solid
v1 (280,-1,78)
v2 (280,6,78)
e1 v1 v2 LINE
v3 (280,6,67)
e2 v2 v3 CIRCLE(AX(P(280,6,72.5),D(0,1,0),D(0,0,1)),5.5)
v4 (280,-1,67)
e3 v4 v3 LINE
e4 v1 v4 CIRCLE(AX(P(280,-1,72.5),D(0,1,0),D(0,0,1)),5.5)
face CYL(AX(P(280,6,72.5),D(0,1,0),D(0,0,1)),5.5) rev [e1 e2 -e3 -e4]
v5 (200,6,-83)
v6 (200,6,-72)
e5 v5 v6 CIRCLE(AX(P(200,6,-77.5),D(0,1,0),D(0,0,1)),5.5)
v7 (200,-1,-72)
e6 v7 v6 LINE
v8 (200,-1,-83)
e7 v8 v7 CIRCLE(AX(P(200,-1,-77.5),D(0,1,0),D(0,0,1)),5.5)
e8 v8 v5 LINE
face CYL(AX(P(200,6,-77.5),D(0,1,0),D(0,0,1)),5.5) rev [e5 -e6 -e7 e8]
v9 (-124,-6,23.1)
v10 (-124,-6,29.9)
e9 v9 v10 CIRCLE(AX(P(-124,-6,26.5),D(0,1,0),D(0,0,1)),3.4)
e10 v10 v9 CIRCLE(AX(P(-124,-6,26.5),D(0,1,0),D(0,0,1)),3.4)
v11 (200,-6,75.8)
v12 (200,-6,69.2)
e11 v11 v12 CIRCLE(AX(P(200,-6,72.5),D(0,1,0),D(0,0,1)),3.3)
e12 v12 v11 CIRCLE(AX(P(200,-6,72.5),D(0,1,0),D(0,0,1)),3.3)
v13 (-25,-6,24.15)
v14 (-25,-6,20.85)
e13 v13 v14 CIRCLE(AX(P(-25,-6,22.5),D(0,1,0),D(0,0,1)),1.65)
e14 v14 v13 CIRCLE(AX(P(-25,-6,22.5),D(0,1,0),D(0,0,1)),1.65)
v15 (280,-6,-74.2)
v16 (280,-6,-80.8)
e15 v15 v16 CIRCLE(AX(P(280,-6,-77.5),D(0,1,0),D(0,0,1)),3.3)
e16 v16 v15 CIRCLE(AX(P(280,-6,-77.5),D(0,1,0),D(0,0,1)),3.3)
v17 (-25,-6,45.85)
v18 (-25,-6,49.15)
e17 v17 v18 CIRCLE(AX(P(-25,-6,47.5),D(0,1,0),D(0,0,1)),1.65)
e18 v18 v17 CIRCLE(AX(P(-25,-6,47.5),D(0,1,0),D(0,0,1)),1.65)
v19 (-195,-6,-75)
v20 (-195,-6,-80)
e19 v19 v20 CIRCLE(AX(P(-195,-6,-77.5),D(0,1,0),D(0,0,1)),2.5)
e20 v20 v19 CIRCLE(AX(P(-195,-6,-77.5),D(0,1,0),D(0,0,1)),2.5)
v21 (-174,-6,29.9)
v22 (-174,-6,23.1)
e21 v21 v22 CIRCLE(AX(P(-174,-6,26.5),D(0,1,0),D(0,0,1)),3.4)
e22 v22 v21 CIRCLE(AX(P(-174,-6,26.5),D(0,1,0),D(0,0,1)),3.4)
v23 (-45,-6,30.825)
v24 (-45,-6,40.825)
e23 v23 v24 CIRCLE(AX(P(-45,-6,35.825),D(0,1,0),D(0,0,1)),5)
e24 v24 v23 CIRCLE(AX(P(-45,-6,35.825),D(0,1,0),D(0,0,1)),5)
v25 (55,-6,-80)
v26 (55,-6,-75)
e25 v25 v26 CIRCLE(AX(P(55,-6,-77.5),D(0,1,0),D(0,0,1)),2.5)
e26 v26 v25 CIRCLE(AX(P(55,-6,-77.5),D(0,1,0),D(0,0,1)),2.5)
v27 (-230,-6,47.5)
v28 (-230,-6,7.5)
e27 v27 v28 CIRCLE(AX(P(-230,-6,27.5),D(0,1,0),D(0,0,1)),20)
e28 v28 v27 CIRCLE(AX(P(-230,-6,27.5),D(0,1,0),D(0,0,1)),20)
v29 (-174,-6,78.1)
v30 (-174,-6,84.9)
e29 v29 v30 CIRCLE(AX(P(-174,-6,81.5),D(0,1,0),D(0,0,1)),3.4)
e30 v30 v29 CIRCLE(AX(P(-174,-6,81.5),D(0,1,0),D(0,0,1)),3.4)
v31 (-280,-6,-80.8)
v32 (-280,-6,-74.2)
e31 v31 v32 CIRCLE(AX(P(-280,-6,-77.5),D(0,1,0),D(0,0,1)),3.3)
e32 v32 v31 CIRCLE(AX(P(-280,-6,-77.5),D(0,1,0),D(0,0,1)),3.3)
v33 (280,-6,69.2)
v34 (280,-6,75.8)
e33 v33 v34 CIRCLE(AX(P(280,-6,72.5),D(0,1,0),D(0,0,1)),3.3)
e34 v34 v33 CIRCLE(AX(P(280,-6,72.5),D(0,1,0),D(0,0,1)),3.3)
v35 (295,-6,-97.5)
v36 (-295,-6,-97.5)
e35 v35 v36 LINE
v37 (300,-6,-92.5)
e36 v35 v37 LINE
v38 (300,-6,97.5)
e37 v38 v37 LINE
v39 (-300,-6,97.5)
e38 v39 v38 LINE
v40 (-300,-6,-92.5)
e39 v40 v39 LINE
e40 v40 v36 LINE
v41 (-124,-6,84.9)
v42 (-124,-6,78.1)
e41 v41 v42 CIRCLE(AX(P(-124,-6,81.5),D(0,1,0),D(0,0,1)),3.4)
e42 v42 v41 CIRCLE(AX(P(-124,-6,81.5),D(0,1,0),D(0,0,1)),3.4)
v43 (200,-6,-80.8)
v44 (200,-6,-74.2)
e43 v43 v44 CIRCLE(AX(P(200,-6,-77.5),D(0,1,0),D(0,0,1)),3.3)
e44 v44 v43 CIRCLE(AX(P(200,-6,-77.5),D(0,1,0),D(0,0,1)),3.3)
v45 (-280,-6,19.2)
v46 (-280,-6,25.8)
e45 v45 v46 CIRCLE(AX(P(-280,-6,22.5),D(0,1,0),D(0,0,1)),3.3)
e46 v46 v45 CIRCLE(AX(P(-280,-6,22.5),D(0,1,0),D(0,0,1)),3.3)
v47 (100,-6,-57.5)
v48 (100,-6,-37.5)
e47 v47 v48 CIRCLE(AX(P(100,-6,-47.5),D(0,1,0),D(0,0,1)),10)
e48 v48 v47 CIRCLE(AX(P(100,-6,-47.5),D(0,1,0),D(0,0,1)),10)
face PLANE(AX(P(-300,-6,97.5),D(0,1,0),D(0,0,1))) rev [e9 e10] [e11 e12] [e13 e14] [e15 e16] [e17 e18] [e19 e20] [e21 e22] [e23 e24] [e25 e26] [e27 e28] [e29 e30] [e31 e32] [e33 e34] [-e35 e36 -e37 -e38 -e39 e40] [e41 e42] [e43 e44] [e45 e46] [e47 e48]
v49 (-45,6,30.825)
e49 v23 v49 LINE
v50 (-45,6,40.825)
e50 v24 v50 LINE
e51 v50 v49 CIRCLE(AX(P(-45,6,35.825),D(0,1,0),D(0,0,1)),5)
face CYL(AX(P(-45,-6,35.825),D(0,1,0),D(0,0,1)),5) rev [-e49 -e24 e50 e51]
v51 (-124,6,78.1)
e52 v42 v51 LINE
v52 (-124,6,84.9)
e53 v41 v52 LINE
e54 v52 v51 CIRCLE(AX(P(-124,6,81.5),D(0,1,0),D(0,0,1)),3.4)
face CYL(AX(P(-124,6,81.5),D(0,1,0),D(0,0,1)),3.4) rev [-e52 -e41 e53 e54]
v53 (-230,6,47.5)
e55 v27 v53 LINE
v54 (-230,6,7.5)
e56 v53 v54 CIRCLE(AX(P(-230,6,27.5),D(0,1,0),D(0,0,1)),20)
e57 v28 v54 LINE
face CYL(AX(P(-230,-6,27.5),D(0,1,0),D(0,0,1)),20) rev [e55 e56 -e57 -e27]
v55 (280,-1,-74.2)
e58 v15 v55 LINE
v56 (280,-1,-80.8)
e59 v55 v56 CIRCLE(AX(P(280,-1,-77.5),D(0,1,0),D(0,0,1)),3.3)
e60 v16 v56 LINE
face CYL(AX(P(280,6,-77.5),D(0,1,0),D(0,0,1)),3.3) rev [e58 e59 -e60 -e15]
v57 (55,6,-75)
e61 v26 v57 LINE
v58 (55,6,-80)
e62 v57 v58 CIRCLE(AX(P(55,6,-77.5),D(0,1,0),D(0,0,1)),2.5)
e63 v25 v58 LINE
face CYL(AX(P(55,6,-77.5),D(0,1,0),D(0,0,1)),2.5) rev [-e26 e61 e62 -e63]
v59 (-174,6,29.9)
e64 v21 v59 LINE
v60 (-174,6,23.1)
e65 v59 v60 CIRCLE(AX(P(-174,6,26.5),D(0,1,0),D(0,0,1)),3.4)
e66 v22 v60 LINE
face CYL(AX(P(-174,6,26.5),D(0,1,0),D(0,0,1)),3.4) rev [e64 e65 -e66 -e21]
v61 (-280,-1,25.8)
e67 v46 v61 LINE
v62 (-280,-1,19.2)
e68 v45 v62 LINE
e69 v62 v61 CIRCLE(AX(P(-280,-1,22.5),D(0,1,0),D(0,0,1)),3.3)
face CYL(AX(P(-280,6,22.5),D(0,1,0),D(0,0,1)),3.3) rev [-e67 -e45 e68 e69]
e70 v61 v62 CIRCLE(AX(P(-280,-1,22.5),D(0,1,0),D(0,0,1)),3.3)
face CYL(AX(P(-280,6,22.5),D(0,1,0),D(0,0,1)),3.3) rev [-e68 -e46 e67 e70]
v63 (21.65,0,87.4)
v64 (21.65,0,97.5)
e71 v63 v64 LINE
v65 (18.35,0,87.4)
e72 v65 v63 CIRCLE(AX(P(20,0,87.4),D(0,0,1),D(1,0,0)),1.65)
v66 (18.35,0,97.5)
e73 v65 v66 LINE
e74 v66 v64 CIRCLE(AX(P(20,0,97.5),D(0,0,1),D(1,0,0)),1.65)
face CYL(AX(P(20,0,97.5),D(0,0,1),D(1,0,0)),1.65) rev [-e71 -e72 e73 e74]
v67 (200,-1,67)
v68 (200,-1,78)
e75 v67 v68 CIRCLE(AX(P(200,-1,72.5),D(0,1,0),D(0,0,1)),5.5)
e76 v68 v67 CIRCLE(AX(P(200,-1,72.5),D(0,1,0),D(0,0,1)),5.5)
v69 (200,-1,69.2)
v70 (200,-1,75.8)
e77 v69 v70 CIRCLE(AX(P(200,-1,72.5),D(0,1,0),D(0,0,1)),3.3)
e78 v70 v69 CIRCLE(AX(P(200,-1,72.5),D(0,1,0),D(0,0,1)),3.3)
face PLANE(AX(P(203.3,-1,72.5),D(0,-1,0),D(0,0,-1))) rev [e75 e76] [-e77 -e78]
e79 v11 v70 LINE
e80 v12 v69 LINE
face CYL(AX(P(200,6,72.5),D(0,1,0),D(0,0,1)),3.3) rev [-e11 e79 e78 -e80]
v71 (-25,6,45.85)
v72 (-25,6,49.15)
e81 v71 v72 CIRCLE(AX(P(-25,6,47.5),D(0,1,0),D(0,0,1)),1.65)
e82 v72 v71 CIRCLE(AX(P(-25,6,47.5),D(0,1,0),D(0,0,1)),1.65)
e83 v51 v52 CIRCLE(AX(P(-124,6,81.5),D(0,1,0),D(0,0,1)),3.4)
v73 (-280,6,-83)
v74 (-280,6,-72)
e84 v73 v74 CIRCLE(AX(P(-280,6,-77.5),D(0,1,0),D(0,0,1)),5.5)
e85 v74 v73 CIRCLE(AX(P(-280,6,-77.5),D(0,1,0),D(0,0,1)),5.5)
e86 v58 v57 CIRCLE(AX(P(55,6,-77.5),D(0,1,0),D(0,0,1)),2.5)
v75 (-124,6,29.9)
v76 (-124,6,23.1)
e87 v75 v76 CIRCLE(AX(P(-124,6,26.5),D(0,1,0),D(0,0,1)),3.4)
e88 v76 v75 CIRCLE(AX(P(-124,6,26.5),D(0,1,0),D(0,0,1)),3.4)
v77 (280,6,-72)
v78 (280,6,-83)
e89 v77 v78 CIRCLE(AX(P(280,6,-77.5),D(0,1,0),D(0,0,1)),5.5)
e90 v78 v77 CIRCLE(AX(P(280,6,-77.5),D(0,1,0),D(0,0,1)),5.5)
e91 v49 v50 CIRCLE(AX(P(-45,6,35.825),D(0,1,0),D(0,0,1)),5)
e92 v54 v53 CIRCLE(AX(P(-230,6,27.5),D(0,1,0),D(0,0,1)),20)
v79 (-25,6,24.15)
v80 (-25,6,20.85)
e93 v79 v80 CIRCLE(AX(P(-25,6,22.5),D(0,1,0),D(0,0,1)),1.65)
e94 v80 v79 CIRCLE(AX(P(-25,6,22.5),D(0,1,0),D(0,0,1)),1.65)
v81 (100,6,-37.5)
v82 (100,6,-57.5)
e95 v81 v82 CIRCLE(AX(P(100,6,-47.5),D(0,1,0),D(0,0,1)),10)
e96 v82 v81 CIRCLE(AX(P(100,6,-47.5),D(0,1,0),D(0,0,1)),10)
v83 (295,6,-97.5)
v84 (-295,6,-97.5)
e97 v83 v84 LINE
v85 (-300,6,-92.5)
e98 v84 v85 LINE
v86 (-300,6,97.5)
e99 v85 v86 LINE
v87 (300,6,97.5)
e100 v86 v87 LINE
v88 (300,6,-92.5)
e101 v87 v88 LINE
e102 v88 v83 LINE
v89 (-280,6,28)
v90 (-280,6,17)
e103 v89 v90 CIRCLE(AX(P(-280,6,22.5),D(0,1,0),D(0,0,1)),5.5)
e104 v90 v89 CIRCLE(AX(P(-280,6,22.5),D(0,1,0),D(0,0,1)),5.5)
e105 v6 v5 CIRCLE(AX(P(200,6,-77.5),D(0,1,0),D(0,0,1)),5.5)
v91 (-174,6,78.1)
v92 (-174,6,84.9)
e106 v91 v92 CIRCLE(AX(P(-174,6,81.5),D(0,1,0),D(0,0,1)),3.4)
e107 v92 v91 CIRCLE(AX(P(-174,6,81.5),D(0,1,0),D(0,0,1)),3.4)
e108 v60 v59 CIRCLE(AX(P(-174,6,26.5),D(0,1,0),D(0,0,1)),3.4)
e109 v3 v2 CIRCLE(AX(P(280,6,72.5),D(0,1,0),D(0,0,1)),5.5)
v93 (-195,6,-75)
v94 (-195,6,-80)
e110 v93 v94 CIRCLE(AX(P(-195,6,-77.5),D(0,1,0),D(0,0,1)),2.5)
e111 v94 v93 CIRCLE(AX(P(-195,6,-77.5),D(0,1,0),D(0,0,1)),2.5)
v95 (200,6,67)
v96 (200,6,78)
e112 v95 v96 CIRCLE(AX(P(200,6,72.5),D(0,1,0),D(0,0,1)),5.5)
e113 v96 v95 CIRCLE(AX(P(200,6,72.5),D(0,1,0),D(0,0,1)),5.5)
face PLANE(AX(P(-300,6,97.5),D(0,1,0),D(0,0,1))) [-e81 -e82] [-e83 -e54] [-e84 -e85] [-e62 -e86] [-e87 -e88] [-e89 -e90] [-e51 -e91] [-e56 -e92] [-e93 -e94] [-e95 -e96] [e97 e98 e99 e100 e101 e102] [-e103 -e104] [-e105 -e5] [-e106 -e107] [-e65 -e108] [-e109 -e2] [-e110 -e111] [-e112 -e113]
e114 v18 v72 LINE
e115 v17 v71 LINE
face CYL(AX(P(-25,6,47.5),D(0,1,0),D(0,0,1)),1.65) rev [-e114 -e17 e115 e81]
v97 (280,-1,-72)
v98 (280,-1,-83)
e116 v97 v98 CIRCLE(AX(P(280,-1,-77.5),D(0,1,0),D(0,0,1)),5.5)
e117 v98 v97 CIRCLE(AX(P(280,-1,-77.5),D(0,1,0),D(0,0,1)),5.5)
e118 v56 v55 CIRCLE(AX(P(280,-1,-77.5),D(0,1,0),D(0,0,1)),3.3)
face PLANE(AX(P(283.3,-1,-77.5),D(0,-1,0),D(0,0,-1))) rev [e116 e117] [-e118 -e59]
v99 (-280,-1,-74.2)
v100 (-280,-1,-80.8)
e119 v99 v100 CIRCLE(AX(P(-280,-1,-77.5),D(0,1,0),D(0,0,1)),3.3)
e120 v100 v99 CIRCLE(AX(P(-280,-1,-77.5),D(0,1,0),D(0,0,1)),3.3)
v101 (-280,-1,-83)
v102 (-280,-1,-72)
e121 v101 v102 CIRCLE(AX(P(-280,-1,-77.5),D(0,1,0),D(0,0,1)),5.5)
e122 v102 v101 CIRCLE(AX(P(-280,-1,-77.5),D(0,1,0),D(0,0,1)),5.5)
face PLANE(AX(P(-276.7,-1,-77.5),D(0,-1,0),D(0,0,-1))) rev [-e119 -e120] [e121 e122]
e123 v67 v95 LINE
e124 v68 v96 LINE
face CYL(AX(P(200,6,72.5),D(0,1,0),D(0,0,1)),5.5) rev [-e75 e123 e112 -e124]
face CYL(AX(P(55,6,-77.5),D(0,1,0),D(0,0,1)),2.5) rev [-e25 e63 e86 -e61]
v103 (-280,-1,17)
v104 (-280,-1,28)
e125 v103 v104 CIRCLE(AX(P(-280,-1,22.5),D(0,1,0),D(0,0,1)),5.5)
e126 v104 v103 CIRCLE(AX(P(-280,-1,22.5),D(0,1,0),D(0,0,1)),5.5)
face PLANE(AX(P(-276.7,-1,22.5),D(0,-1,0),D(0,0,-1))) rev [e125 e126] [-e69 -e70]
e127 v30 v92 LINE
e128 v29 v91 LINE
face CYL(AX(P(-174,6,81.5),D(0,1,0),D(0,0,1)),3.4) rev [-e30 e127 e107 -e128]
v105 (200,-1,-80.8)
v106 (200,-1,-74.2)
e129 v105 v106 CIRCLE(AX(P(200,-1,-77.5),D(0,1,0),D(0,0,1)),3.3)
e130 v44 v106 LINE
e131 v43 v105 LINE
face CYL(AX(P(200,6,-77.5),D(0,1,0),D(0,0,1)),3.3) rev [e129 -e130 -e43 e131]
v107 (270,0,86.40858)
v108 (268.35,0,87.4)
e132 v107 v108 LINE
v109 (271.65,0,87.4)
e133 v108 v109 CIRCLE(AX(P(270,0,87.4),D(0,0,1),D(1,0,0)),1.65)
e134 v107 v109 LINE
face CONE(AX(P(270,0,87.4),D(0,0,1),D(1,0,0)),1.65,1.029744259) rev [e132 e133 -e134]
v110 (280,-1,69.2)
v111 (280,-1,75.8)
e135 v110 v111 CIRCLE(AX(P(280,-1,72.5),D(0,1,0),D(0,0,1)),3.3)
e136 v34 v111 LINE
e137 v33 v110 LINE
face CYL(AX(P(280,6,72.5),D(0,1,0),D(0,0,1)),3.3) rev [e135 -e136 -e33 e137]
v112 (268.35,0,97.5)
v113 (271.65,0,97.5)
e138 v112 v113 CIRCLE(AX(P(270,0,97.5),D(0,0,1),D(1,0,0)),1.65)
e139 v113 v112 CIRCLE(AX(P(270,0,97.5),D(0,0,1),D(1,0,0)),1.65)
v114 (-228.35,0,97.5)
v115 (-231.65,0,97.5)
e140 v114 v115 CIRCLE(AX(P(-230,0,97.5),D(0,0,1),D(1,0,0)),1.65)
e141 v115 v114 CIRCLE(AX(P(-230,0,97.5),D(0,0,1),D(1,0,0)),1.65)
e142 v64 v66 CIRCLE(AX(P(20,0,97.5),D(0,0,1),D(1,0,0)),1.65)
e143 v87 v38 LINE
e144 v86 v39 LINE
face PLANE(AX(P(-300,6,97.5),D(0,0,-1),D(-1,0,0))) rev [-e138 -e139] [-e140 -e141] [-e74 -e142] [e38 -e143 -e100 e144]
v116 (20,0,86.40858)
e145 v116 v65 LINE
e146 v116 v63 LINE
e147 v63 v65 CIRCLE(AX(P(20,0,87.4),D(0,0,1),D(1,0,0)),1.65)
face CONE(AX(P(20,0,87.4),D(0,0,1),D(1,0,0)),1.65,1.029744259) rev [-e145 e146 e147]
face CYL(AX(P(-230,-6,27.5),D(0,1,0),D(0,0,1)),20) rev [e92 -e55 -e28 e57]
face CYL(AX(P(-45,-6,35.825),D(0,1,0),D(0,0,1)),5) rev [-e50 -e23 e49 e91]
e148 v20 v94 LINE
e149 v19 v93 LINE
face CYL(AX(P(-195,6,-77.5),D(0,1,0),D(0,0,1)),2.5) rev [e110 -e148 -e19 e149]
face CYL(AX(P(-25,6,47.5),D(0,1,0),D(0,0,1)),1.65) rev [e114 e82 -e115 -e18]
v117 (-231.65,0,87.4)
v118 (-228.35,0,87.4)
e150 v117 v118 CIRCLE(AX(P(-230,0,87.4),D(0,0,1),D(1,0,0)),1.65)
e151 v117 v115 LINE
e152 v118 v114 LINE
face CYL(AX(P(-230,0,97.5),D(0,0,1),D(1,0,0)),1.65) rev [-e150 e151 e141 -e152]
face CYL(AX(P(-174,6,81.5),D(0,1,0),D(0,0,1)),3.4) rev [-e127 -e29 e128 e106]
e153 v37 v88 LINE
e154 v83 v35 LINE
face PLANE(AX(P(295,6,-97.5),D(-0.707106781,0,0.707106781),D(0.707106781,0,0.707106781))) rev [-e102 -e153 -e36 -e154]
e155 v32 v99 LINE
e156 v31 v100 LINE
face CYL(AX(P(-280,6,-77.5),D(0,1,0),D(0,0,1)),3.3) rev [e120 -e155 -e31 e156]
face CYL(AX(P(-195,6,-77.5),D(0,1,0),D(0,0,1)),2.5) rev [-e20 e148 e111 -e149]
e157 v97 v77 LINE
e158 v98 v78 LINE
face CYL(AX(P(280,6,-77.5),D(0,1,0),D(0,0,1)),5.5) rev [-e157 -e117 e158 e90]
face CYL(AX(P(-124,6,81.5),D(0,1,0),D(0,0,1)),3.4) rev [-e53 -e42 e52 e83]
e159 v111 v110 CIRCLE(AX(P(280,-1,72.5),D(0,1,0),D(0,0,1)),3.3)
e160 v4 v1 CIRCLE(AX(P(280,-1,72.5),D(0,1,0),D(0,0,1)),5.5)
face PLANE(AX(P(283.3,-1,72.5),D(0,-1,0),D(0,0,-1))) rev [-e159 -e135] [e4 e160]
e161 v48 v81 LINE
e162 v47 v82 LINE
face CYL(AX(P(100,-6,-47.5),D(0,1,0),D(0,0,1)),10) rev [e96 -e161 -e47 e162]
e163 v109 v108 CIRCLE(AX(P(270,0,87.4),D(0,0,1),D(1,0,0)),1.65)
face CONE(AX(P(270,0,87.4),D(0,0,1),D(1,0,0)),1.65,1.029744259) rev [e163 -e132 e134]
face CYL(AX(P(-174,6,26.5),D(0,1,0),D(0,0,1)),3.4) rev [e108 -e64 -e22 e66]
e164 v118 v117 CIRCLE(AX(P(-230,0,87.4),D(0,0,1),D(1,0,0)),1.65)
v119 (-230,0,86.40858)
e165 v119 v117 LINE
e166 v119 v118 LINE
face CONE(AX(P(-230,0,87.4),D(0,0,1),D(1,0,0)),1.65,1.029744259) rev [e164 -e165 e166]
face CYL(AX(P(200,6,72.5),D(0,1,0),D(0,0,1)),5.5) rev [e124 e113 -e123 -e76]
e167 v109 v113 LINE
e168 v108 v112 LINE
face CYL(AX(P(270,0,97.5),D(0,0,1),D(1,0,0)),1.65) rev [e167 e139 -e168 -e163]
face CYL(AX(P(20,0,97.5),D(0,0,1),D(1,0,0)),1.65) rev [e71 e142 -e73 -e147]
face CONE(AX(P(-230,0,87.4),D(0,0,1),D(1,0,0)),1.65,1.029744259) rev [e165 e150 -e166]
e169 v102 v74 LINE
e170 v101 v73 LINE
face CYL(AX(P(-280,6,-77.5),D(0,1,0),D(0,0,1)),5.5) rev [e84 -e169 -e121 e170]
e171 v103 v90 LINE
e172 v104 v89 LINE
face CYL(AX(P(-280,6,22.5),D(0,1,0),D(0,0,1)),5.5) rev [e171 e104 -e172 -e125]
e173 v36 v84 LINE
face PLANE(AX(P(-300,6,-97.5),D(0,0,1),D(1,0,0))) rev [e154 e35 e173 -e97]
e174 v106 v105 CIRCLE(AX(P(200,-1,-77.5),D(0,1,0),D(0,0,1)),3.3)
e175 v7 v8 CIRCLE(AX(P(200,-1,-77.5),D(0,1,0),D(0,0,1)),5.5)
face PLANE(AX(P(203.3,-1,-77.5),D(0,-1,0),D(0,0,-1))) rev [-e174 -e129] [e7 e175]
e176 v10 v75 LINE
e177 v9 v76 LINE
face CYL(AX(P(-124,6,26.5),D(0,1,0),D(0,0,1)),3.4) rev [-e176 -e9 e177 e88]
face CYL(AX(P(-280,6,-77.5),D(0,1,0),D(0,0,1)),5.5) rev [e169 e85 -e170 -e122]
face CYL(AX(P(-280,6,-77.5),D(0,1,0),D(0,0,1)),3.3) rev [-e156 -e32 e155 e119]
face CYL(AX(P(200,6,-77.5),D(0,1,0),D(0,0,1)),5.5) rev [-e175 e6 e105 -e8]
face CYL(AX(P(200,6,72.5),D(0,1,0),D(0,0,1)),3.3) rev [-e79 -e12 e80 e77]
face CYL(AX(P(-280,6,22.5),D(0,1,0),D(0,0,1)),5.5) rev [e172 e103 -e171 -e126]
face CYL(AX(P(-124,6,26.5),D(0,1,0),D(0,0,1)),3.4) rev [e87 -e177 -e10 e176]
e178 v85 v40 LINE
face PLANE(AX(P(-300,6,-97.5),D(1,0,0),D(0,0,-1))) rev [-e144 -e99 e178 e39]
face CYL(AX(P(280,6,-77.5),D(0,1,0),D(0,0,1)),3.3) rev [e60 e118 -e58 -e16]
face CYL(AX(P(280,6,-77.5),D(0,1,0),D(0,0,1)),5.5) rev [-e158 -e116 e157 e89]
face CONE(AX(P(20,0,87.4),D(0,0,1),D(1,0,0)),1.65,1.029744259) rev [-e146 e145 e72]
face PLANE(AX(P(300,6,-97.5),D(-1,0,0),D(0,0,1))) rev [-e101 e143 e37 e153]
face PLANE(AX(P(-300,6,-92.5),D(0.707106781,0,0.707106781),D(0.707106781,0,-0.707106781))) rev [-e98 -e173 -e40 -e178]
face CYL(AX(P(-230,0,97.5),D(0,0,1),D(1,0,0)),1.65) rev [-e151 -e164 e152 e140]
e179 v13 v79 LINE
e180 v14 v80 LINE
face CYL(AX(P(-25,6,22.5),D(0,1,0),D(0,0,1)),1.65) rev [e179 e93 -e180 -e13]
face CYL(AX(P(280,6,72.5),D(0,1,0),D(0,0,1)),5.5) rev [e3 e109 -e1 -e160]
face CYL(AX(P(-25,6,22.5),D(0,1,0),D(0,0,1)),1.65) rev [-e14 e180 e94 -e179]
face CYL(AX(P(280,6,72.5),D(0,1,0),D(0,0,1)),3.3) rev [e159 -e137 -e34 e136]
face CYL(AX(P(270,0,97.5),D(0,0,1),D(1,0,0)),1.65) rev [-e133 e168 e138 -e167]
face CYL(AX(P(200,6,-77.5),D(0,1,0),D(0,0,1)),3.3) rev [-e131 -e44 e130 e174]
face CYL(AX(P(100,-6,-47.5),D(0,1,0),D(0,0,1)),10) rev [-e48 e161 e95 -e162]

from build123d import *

# Parameters (mm, degrees)
SKETCH1_W                                         = 600
SKETCH1_H                                         = 195
EXTRUDE1_DEPTH                                    = 6
CHAMFER1_SIZE                                     = 5
M6_SOCKET_HEAD_CAP_SCREW_COUNTERBORE1_D           = 6.6
M6_SOCKET_HEAD_CAP_SCREW_COUNTERBORE1_CBORE_D     = 11
M6_SOCKET_HEAD_CAP_SCREW_COUNTERBORE1_CBORE_DEPTH = 7
M4_TAPPED_HOLE1_D                                 = 3.3
M4_TAPPED_HOLE1_DEPTH                             = 10.1
M4_TAPPED_HOLE1_TIP                               = 0.991420021
M8_TAPPED_HOLE1_D                                 = 6.8
M6_TAPPED_HOLE2_D                                 = 5
SKETCH10_R                                        = 20
CUT_EXTRUDE1_DEPTH                                = 316.674278331
SKETCH11_R                                        = 10
CUT_EXTRUDE2_DEPTH                                = 316.674278331
M4_TAPPED_HOLE2_D                                 = 3.3
M4_TAPPED_HOLE2_DEPTH                             = 12
M4_TAPPED_HOLE2_TIP                               = 0.991420021
SKETCH13_R                                        = 5
CUT_EXTRUDE3_DEPTH                                = 316.674278331


with BuildPart() as part:
    # Sketch1 → Extrude1 (new, symmetric)
    with BuildSketch(Plane(origin=(0, 0, 0), x_dir=(1, 0, 0), z_dir=(0, 1, 0))):
        Rectangle(SKETCH1_W, SKETCH1_H)
    extrude(amount=EXTRUDE1_DEPTH, both=True)

    # Chamfer1
    chamfer1_edges = [part.edges().sort_by_distance(p)[0] for p in [
        (-300, 0, -97.5),
        (300, 0, -97.5),
    ]]
    chamfer(chamfer1_edges, length=CHAMFER1_SIZE)

    # M6 Socket Head Cap Screw Counterbore1 (through all)
    with Locations(Plane(origin=(-280, 6, -77.5), x_dir=(0, 0, 1), z_dir=(0, 1, 0))):
        with Locations((0, 0), (100, 0), (0, 480), (0, 560), (150, 560), (150, 480)):
            CounterBoreHole(M6_SOCKET_HEAD_CAP_SCREW_COUNTERBORE1_D / 2, M6_SOCKET_HEAD_CAP_SCREW_COUNTERBORE1_CBORE_D / 2, M6_SOCKET_HEAD_CAP_SCREW_COUNTERBORE1_CBORE_DEPTH)

    # M4 Tapped Hole1
    with Locations(Plane(origin=(-230, 0, 97.5), x_dir=(1, 0, 0), z_dir=(0, 0, 1))):
        with Locations((0, 0), (250, 0), (500, 0)):
            Hole(M4_TAPPED_HOLE1_D / 2, depth=M4_TAPPED_HOLE1_DEPTH)
            with Locations((0, 0, -(M4_TAPPED_HOLE1_DEPTH + M4_TAPPED_HOLE1_TIP / 2))):  # 118° drill point
                Cone(0, M4_TAPPED_HOLE1_D / 2, M4_TAPPED_HOLE1_TIP, mode=Mode.SUBTRACT)

    # M8 Tapped Hole1 (through all)
    with Locations(Plane(origin=(-174, 6, 81.5), x_dir=(0, 0, 1), z_dir=(0, 1, 0))):
        with Locations((0, 0), (0, 50), (-55, 50), (-55, 0)):
            Hole(M8_TAPPED_HOLE1_D / 2)

    # M6 Tapped Hole2 (through all)
    with Locations(Plane(origin=(55, 6, -77.5), x_dir=(0, 0, 1), z_dir=(0, 1, 0))):
        with Locations((0, 0), (0, -250)):
            Hole(M6_TAPPED_HOLE2_D / 2)

    # Sketch10 → Cut-Extrude1 (cut, through all)
    with BuildSketch(Plane(origin=(0, 6, 0), x_dir=(1, 0, 0), z_dir=(0, 1, 0))):
        with Locations(Location((-230, -27.5, 0), (0, 0, 270))):
            Circle(SKETCH10_R)
    extrude(amount=-CUT_EXTRUDE1_DEPTH, mode=Mode.SUBTRACT)

    # Sketch11 → Cut-Extrude2 (cut, through all)
    with BuildSketch(Plane(origin=(0, 6, 0), x_dir=(1, 0, 0), z_dir=(0, 1, 0))):
        with Locations(Location((100, 47.5, 0), (0, 0, 270))):
            Circle(SKETCH11_R)
    extrude(amount=-CUT_EXTRUDE2_DEPTH, mode=Mode.SUBTRACT)

    # M4 Tapped Hole2
    with Locations(Plane(origin=(-25, 6, 47.5), x_dir=(0, 0, 1), z_dir=(0, 1, 0))):
        with Locations((0, 0), (-25, 0)):
            Hole(M4_TAPPED_HOLE2_D / 2, depth=M4_TAPPED_HOLE2_DEPTH)
            with Locations((0, 0, -(M4_TAPPED_HOLE2_DEPTH + M4_TAPPED_HOLE2_TIP / 2))):  # 118° drill point
                Cone(0, M4_TAPPED_HOLE2_D / 2, M4_TAPPED_HOLE2_TIP, mode=Mode.SUBTRACT)

    # Sketch13 → Cut-Extrude3 (cut, through all)
    with BuildSketch(Plane(origin=(0, 6, 0), x_dir=(1, 0, 0), z_dir=(0, 1, 0))):
        with Locations(Location((-45, -35.825, 0), (0, 0, 270))):
            Circle(SKETCH13_R)
    extrude(amount=-CUT_EXTRUDE3_DEPTH, mode=Mode.SUBTRACT)


solid = part.part
